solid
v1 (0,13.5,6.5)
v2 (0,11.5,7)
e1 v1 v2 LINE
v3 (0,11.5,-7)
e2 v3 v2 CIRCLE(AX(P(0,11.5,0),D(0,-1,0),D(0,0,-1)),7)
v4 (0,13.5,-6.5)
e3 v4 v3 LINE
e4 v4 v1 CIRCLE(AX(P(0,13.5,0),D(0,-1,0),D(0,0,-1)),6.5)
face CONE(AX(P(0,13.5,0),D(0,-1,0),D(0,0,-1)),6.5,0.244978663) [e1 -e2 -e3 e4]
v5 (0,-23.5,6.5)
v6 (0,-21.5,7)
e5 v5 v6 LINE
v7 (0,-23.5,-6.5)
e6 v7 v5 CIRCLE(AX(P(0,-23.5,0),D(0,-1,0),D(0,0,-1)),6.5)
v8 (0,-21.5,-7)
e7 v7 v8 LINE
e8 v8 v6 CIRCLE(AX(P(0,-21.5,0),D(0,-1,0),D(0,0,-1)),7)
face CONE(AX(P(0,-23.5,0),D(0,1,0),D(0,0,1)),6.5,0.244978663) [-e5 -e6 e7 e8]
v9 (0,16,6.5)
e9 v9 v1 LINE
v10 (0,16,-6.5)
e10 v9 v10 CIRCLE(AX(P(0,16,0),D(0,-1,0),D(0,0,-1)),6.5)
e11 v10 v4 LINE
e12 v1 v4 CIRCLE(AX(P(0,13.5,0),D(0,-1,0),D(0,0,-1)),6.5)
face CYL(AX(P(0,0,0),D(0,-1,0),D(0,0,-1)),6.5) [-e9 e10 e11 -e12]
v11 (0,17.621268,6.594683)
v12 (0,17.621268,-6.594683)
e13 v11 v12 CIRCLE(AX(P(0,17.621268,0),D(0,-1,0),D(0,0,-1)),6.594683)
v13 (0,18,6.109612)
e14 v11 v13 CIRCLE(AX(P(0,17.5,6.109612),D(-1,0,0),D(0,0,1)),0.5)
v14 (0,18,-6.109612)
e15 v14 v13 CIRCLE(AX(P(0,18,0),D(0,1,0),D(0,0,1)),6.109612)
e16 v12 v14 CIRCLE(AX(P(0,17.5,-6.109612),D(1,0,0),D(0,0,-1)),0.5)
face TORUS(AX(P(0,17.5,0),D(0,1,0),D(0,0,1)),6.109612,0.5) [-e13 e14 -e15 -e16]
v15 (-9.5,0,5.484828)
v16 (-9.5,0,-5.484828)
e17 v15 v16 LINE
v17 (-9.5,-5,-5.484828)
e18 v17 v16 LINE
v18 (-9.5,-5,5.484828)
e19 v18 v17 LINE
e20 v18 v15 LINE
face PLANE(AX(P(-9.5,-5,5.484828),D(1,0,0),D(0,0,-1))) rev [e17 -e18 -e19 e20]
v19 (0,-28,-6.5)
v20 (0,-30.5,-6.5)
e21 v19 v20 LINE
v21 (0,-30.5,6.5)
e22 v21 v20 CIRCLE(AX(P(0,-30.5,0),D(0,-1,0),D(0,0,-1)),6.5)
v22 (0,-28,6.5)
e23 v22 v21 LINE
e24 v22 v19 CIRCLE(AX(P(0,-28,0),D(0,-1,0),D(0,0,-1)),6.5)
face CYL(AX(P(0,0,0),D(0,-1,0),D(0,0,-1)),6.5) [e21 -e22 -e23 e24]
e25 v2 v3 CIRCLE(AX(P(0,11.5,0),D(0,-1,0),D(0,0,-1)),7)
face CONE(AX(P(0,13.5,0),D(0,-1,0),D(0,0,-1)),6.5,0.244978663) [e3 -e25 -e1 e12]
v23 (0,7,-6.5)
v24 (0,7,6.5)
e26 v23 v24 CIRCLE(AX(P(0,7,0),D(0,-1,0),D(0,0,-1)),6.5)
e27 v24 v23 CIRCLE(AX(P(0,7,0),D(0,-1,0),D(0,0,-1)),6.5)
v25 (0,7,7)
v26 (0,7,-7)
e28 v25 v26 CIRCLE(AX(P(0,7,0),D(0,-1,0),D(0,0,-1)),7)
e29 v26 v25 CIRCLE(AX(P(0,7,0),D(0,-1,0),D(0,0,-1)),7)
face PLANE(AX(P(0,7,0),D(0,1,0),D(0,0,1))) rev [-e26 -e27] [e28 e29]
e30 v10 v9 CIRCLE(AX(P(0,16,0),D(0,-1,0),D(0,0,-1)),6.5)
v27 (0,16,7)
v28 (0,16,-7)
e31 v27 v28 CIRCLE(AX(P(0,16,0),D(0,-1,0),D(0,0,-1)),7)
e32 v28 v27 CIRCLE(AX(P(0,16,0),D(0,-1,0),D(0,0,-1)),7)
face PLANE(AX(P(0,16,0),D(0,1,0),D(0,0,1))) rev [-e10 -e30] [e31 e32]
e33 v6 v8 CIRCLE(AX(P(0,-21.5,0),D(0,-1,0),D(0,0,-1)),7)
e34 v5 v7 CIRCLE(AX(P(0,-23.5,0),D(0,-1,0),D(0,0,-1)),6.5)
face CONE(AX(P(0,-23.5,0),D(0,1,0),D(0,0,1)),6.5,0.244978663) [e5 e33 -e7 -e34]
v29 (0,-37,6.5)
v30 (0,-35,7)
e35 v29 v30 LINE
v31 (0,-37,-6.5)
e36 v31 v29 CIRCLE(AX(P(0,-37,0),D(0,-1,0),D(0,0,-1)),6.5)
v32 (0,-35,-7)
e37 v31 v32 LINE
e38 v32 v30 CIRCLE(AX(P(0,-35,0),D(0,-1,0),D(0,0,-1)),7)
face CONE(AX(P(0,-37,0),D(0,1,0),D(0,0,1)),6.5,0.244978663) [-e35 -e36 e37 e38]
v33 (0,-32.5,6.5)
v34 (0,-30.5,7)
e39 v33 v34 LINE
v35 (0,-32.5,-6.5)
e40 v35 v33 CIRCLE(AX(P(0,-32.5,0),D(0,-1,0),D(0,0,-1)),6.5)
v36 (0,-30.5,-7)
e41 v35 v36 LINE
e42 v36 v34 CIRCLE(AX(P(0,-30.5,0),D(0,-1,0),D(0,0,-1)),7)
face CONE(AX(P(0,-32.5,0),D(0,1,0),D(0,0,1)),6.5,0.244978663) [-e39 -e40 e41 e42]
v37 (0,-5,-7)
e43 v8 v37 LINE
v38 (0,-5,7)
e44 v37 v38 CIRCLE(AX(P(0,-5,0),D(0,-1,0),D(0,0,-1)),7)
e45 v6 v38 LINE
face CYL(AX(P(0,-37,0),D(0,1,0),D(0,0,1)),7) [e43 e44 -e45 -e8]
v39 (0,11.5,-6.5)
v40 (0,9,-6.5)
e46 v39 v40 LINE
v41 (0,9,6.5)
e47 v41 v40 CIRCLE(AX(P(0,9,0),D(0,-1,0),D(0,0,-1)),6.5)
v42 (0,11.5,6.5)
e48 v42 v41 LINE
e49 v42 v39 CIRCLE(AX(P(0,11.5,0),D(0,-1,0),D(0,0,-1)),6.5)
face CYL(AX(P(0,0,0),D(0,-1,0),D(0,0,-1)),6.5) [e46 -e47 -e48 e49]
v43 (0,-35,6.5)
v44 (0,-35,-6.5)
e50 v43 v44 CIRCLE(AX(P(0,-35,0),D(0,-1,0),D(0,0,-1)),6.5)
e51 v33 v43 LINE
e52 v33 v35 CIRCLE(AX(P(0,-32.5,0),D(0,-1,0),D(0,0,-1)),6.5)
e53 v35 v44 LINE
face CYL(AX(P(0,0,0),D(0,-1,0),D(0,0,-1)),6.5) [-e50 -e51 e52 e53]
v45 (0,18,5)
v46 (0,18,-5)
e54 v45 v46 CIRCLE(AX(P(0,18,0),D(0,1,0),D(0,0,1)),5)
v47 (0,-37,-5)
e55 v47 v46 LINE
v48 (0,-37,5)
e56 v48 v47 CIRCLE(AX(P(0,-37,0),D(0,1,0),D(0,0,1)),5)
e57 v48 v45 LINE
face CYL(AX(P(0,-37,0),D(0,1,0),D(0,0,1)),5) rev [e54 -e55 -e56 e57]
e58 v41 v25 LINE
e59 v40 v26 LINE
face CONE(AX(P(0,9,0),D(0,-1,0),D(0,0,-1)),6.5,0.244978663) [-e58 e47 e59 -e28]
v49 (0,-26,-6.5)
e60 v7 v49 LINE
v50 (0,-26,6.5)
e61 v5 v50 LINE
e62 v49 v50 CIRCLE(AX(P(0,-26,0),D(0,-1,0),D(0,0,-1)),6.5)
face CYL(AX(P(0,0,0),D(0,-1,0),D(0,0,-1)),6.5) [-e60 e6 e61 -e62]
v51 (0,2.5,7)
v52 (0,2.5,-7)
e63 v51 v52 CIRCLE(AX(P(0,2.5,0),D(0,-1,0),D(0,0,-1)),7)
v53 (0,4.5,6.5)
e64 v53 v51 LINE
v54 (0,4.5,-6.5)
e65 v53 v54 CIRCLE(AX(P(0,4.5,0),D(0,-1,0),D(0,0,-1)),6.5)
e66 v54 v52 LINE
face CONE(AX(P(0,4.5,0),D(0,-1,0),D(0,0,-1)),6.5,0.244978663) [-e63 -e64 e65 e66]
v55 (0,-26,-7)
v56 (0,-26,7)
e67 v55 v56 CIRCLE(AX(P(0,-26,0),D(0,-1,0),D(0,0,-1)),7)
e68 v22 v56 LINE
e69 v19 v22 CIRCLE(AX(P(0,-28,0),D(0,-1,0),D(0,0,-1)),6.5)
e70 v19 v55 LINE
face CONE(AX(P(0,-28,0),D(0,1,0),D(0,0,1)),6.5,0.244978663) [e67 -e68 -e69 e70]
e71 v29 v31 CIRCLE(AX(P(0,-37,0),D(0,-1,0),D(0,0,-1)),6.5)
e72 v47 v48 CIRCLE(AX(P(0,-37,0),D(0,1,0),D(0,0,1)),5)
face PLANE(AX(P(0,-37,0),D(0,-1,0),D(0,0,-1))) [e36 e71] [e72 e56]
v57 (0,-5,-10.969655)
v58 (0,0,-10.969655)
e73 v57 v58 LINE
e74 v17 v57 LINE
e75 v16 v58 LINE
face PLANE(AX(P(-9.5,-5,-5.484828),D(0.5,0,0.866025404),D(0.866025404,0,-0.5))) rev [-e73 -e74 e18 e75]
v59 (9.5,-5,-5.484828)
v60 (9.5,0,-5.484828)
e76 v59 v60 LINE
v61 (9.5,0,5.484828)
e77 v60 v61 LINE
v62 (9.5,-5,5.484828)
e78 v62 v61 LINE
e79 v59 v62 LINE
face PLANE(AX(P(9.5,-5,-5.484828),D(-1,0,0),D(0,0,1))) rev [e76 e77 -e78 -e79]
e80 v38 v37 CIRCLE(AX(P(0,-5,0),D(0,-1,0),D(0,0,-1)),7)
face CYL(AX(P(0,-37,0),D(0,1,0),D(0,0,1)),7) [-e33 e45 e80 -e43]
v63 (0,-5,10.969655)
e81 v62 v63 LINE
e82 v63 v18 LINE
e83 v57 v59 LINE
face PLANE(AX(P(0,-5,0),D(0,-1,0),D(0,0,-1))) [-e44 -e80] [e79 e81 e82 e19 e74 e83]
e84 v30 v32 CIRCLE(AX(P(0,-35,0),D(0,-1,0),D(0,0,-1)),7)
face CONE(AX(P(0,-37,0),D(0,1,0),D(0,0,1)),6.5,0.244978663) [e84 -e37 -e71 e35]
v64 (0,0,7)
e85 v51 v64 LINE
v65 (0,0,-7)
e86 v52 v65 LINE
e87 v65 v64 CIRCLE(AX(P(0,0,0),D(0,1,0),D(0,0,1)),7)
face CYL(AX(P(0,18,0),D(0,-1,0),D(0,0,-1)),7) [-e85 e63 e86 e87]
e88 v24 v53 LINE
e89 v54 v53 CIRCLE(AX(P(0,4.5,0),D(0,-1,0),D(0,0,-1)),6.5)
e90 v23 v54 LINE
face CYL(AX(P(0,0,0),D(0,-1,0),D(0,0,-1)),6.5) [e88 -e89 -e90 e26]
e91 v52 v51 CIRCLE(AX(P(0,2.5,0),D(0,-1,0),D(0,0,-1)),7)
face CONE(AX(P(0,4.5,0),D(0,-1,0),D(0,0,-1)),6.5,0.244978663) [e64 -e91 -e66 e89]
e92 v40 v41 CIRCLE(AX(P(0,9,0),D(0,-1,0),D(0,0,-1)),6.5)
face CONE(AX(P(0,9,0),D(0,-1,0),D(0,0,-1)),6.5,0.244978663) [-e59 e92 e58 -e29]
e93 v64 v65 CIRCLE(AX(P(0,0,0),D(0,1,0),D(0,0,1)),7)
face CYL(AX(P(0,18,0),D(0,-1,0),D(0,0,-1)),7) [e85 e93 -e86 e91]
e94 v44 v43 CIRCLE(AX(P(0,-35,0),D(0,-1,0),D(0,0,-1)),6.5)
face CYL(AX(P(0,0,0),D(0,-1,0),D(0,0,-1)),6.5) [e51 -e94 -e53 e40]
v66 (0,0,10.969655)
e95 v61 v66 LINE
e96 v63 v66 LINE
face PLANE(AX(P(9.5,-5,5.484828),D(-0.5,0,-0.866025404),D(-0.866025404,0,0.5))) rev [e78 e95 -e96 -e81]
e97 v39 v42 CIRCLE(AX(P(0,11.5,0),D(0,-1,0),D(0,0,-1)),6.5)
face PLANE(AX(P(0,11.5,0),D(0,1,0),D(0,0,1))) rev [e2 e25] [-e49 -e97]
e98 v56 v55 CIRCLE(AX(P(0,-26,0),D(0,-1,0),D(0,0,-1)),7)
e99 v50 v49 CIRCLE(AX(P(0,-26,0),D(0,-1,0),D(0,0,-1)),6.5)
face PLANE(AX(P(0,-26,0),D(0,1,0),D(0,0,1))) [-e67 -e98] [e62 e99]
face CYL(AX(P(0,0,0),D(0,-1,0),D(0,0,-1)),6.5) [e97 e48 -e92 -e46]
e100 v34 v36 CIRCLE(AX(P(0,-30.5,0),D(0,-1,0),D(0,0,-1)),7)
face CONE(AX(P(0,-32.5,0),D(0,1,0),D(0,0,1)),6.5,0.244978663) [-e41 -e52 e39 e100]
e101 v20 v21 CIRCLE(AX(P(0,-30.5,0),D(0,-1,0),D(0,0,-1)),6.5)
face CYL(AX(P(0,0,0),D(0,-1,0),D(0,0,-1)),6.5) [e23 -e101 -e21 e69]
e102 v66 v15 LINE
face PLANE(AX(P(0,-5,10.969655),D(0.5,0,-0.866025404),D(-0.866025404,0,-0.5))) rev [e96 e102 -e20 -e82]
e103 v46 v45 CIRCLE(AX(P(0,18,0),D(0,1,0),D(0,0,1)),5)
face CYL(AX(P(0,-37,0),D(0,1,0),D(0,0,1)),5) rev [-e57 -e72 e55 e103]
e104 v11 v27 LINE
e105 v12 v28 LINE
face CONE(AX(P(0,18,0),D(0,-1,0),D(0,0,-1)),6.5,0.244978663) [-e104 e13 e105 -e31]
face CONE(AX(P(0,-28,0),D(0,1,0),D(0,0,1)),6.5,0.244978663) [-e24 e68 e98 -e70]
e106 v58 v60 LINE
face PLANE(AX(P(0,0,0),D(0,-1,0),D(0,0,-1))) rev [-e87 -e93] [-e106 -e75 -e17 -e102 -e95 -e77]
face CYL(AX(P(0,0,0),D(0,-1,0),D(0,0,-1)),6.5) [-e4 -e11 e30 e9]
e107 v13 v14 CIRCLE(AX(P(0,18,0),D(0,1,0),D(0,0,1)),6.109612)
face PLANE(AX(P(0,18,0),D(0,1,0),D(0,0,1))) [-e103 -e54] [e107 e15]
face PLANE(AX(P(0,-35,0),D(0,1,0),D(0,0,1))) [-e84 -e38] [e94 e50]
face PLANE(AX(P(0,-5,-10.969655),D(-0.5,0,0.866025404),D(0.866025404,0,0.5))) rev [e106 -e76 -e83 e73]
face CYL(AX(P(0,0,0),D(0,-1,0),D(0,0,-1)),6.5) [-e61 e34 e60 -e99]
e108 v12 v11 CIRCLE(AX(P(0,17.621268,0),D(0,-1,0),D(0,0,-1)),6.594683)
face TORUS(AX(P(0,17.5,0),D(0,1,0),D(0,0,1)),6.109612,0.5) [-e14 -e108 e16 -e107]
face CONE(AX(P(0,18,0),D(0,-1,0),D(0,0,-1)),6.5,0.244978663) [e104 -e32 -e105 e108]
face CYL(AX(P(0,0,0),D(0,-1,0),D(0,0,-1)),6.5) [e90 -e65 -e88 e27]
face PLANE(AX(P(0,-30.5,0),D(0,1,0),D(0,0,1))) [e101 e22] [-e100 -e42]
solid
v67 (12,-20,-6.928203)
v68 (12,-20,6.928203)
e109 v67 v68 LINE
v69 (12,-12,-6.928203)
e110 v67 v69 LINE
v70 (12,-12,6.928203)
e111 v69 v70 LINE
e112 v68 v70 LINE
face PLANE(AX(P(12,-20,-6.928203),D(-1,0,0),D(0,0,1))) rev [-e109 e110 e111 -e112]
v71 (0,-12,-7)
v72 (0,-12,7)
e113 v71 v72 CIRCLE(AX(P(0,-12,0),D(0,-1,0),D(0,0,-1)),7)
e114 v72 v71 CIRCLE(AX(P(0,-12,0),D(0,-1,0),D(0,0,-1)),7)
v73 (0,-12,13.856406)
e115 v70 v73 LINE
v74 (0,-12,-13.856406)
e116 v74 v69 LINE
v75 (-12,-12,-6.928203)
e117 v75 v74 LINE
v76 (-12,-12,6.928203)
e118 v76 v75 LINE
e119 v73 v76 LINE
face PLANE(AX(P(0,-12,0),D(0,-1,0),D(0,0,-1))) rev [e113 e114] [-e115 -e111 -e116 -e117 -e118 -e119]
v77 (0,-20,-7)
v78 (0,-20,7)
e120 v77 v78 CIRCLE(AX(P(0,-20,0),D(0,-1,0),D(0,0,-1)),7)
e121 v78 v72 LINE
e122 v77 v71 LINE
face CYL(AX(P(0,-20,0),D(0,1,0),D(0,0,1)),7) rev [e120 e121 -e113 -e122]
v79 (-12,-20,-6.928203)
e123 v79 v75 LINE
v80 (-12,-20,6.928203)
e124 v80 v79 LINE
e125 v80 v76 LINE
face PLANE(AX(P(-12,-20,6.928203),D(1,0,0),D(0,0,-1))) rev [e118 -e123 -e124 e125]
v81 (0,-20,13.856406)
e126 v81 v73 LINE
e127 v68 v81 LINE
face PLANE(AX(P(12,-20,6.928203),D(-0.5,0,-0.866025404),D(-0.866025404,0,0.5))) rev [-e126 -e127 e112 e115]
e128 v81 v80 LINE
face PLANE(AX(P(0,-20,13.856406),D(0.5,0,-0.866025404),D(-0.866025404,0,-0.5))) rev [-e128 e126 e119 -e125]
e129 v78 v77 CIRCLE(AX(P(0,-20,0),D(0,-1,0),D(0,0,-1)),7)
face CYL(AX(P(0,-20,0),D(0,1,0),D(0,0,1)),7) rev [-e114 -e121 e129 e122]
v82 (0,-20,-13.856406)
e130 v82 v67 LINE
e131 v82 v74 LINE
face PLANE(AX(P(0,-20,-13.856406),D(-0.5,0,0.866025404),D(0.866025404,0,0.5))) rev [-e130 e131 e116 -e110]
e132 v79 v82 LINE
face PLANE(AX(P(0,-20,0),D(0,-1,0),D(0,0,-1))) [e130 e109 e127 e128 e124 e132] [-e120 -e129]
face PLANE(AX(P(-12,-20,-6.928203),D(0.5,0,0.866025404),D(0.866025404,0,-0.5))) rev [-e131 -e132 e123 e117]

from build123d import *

# Parameters (mm, degrees)
SKETCH2_R           = 7
BOSS_EXTRUDE1_DEPTH = 18
BOSS_EXTRUDE2_DEPTH = 5
BOSS_EXTRUDE3_START = 32
SKETCH6_R           = 7
BOSS_EXTRUDE3_DEPTH = 32
SKETCH4_R           = 5
CUT_EXTRUDE1_DEPTH  = 57.88218819
FILLET1_R           = 0.5
SKETCH8_R           = 7
BOSS_EXTRUDE4_DEPTH = 8


with BuildPart() as part:
    # Sketch2 → Boss-Extrude1 (new body)
    with BuildSketch(Plane(origin=(0, 0, 0), x_dir=(1, 0, 0), z_dir=(0, 1, 0))):
        with Locations(Location((0, 0, 0), (0, 0, 270))):
            Circle(SKETCH2_R)
    extrude(amount=BOSS_EXTRUDE1_DEPTH)

    # Sketch5 → Boss-Extrude2 (add)
    with BuildSketch(Plane.XZ):
        Polygon((9.5, -5.484827557), (9.5, 5.484827557), (0, 10.969655115), (-9.5, 5.484827557), (-9.5, -5.484827557), (0, -10.969655115), align=None)
    extrude(amount=BOSS_EXTRUDE2_DEPTH)

    # Sketch6 → Boss-Extrude3 (add)
    with BuildSketch(Plane.XZ.offset(5).offset(BOSS_EXTRUDE3_START)):
        with Locations(Location((0, 0, 0), (0, 0, 90))):
            Circle(SKETCH6_R)
    extrude(amount=-BOSS_EXTRUDE3_DEPTH)

    # Sketch4 → Cut-Extrude1 (cut, through all)
    with BuildSketch(Plane(origin=(0, 18, 0), x_dir=(1, 0, 0), z_dir=(0, 1, 0))):
        with Locations(Location((0, 0, 0), (0, 0, 270))):
            Circle(SKETCH4_R)
    extrude(amount=-CUT_EXTRUDE1_DEPTH, mode=Mode.SUBTRACT)

    # Sketch3 → Cut-Revolve1 (revolve, cut)
    with BuildSketch(Plane.XY, mode=Mode.PRIVATE) as cut_revolve1_sk:
        Polygon((6.5, 18), (7, 16), (6.5, 16), (6.5, 13.5), (7, 11.5), (6.5, 11.5), (6.5, 9), (7, 7), (6.5, 7), (6.5, 4.5), (7, 2.5), (7, 18), align=None)
        Polygon((6.5, -23.5), (7, -21.5), (7, -37), (6.5, -37), (7, -35), (6.5, -35), (6.5, -32.5), (7, -30.5), (6.5, -30.5), (6.5, -28), (7, -26), (6.5, -26), align=None)
    revolve(cut_revolve1_sk.sketch.rotate(Axis((0, 0, 0), (0, 1, 0)), 90), axis=Axis((0, 0, 0), (0, 1, 0)), mode=Mode.SUBTRACT)

    # Fillet1
    fillet1_edges = [part.edges().sort_by_distance(p)[0] for p in [
        (0, 18, 6.5),
    ]]
    fillet(fillet1_edges, radius=FILLET1_R)


with BuildPart() as body_2:
    # Sketch8 → Boss-Extrude4 (new body)
    with BuildSketch(Plane(origin=(0, -12, 0), x_dir=(-1, 0, 0), z_dir=(0, -1, 0))):
        Polygon((0, 13.856406461), (-12, 6.92820323), (-12, -6.92820323), (0, -13.856406461), (12, -6.92820323), (12, 6.92820323), align=None)
        with Locations(Location((0, 0, 0), (0, 0, 90))):
            Circle(SKETCH8_R, mode=Mode.SUBTRACT)
    extrude(amount=BOSS_EXTRUDE4_DEPTH)


solid = Compound([part.part, body_2.part])
